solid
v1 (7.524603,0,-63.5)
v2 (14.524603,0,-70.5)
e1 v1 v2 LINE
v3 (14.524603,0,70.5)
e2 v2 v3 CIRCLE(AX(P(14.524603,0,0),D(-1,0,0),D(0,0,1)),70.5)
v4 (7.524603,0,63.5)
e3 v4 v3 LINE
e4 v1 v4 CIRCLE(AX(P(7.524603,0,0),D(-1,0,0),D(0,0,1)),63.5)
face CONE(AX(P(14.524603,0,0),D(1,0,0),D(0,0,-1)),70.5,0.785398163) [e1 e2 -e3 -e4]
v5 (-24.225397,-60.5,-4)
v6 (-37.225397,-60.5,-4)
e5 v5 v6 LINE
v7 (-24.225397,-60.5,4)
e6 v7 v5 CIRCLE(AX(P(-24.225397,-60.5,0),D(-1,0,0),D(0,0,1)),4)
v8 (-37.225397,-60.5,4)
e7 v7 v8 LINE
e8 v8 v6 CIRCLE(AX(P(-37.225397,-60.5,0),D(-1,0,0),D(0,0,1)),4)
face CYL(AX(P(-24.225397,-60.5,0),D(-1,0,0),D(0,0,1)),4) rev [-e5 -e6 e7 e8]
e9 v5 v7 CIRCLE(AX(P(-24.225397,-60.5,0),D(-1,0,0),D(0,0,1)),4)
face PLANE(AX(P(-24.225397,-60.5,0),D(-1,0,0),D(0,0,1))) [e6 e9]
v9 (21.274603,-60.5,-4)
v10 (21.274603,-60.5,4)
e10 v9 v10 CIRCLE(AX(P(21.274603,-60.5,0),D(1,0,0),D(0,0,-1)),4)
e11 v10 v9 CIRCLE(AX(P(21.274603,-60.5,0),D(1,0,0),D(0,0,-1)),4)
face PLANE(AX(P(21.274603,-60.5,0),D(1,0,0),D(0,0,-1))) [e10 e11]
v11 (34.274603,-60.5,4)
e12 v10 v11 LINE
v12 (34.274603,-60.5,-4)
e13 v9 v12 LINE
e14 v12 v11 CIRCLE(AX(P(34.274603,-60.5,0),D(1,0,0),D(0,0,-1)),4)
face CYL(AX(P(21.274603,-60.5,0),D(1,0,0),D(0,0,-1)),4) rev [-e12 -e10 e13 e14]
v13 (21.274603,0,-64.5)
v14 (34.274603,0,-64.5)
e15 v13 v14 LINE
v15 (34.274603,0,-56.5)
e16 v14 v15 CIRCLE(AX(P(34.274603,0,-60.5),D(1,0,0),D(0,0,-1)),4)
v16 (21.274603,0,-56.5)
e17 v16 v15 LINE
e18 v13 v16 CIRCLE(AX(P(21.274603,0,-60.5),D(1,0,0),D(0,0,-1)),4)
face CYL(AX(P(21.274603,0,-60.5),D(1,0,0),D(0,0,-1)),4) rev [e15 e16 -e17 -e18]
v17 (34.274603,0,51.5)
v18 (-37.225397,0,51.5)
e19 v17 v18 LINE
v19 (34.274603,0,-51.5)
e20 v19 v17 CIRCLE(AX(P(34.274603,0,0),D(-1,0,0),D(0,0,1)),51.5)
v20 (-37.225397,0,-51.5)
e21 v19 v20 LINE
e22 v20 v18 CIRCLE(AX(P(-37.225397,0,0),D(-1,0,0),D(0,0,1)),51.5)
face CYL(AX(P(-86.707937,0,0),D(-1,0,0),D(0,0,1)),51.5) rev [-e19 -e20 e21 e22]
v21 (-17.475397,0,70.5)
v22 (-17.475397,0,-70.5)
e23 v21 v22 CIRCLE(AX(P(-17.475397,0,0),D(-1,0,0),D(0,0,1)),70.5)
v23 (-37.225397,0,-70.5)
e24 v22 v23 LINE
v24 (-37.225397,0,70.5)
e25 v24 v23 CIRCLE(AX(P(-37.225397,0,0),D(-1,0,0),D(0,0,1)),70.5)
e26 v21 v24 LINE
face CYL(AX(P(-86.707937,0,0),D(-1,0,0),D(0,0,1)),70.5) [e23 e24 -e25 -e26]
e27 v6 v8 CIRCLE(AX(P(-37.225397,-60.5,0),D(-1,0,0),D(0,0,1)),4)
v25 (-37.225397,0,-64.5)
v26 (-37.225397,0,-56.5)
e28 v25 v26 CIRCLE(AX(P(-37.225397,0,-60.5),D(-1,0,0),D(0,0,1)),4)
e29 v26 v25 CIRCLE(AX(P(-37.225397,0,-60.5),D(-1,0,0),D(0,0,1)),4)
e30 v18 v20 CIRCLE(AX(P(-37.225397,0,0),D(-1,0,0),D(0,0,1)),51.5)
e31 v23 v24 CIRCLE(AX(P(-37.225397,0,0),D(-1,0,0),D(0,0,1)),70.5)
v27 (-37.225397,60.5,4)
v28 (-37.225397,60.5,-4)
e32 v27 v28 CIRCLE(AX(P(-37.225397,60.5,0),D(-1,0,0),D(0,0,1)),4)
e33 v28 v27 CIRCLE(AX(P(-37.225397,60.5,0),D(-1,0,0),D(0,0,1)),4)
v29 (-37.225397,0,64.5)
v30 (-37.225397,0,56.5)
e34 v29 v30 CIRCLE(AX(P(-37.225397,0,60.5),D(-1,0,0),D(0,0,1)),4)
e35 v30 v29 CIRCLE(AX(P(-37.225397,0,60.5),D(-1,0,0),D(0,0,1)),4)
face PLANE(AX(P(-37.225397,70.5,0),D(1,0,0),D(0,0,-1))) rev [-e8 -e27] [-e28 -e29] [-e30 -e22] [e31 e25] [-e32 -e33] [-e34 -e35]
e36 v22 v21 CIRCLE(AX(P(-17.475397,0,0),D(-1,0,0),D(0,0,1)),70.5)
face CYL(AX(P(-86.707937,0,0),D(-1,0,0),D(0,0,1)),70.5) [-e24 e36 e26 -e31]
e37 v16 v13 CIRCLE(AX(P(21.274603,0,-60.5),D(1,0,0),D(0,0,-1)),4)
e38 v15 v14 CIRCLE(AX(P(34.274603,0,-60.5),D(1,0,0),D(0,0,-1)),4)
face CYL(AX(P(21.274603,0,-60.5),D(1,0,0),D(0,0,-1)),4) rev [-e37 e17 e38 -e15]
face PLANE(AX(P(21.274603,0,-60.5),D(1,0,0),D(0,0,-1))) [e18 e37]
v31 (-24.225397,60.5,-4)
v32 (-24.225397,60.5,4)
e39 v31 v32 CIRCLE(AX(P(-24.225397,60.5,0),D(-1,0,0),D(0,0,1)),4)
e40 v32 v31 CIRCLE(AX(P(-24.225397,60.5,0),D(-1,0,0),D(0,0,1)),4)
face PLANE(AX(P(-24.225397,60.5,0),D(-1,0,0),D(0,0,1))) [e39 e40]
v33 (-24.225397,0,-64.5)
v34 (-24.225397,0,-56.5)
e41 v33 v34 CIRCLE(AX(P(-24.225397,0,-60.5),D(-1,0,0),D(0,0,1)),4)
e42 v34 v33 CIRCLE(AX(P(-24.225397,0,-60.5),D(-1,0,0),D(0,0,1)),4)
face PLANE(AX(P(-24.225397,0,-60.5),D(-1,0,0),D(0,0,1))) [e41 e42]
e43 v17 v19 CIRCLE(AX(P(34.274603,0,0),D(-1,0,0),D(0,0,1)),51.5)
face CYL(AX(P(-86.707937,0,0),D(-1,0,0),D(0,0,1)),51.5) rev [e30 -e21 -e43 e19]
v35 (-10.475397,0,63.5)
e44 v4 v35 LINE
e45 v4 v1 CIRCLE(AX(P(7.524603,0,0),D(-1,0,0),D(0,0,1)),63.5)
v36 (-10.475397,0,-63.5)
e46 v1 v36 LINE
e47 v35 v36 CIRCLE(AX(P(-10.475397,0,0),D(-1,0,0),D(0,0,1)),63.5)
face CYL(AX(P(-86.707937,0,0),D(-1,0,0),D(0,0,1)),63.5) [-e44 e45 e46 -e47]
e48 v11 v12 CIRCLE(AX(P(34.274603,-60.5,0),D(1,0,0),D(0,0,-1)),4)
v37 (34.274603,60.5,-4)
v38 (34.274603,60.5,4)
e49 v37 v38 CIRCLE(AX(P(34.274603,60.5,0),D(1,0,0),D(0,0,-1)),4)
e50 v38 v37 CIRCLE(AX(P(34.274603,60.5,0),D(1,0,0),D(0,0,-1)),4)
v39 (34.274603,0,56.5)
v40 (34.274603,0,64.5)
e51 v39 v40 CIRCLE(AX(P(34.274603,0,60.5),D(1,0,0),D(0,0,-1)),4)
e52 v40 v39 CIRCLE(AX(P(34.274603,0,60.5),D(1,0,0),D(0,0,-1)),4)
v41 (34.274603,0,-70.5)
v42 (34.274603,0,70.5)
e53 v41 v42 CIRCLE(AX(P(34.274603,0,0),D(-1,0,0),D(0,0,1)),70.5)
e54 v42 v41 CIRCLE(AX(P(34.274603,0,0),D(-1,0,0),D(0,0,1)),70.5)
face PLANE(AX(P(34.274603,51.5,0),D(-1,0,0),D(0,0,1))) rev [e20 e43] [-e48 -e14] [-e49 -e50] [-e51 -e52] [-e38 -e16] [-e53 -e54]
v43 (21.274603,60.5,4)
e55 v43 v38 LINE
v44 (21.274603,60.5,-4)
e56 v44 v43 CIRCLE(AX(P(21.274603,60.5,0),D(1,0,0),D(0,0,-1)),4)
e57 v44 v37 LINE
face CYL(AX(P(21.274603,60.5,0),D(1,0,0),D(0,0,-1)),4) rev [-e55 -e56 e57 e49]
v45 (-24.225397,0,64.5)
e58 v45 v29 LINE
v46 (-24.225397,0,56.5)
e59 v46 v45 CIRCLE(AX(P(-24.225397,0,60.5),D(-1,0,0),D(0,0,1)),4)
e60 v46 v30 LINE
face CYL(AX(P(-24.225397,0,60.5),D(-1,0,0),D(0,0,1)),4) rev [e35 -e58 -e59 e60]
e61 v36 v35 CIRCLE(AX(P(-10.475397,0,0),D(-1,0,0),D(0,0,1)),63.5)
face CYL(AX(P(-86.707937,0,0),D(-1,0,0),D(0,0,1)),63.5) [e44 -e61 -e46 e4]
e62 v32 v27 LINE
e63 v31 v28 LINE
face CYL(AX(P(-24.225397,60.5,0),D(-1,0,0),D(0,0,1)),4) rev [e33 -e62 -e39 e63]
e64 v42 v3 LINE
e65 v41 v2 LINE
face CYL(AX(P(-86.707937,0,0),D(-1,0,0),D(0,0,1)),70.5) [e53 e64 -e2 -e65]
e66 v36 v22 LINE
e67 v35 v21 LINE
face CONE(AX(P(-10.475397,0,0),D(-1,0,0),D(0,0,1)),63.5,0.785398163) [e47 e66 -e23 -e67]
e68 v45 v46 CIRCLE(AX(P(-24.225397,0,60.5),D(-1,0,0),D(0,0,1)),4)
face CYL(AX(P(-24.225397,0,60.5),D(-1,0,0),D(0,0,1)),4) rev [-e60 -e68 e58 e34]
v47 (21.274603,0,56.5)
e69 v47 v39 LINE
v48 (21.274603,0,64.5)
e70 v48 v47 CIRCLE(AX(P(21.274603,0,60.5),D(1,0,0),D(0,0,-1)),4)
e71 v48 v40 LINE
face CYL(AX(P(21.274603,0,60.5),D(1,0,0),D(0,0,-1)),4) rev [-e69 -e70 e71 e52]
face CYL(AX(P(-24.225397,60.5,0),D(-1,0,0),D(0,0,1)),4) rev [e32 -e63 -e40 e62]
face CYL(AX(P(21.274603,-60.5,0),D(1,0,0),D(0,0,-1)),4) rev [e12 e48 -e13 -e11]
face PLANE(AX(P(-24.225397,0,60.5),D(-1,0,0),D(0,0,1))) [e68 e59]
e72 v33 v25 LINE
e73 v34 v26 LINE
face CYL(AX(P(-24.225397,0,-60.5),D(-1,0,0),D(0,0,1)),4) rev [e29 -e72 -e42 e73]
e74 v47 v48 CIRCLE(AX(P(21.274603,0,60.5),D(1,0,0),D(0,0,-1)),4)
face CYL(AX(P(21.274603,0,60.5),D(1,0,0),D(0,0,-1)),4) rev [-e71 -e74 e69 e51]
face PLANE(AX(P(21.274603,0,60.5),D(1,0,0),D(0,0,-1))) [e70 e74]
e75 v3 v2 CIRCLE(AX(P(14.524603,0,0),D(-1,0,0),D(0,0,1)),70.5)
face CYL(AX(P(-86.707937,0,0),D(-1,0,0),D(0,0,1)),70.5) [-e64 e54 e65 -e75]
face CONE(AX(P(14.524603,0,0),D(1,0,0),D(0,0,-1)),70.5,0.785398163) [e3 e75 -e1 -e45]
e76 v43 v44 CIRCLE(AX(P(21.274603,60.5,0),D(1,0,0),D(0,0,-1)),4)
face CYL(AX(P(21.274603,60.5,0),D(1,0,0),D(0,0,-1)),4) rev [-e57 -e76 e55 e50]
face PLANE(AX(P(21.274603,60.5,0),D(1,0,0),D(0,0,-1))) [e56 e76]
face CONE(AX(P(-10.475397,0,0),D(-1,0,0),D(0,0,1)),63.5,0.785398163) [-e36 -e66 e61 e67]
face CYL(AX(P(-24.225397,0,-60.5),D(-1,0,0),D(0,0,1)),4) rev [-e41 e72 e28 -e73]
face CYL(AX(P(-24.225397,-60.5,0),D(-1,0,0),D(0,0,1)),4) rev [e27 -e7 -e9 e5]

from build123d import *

# Parameters (mm, degrees)
SKETCH4_R          = 4
CUT_EXTRUDE1_DEPTH = 13
CUT_EXTRUDE2_START = -13
SKETCH5_R          = 4
CUT_EXTRUDE2_DEPTH = 13


with BuildPart() as part:
    # Sketch2 → Revolve1 (revolve)
    with BuildSketch(Plane.XY, mode=Mode.PRIVATE) as revolve1_sk:
        Polygon((-37.225396825, 70.5), (-37.225396825, 51.5), (34.274603175, 51.5), (34.274603175, 70.5), (14.524603175, 70.5), (7.524603175, 63.5), (-10.475396825, 63.5), (-17.475396825, 70.5), align=None)
    revolve(revolve1_sk.sketch.rotate(Axis((-86.707936508, 0, 0), (1, 0, 0)), 90), axis=Axis((-86.707936508, 0, 0), (1, 0, 0)))

    # Sketch4 → Cut-Extrude1 (cut)
    with BuildSketch(Plane.ZY.offset(37.225396825)):
        with Locations((0, -60.5)):
            Circle(SKETCH4_R)
        with Locations((-60.5, 0)):
            Circle(SKETCH4_R)
        with Locations((0, 60.5)):
            Circle(SKETCH4_R)
        with Locations((60.5, 0)):
            Circle(SKETCH4_R)
    extrude(amount=-CUT_EXTRUDE1_DEPTH, mode=Mode.SUBTRACT)

    # Sketch5 → Cut-Extrude2 (cut)
    with BuildSketch(Plane(origin=(34.274603175, 0, 0), x_dir=(0, 0, -1), z_dir=(1, 0, 0)).offset(CUT_EXTRUDE2_START)):
        with Locations(Location((0, -60.5, 0), (0, 0, 180))):
            Circle(SKETCH5_R)
        with Locations(Location((-60.5, 0, 0), (0, 0, 180))):
            Circle(SKETCH5_R)
        with Locations(Location((0, 60.5, 0), (0, 0, 180))):
            Circle(SKETCH5_R)
        with Locations(Location((60.5, 0, 0), (0, 0, 180))):
            Circle(SKETCH5_R)
    extrude(amount=CUT_EXTRUDE2_DEPTH, mode=Mode.SUBTRACT)


solid = part.part
